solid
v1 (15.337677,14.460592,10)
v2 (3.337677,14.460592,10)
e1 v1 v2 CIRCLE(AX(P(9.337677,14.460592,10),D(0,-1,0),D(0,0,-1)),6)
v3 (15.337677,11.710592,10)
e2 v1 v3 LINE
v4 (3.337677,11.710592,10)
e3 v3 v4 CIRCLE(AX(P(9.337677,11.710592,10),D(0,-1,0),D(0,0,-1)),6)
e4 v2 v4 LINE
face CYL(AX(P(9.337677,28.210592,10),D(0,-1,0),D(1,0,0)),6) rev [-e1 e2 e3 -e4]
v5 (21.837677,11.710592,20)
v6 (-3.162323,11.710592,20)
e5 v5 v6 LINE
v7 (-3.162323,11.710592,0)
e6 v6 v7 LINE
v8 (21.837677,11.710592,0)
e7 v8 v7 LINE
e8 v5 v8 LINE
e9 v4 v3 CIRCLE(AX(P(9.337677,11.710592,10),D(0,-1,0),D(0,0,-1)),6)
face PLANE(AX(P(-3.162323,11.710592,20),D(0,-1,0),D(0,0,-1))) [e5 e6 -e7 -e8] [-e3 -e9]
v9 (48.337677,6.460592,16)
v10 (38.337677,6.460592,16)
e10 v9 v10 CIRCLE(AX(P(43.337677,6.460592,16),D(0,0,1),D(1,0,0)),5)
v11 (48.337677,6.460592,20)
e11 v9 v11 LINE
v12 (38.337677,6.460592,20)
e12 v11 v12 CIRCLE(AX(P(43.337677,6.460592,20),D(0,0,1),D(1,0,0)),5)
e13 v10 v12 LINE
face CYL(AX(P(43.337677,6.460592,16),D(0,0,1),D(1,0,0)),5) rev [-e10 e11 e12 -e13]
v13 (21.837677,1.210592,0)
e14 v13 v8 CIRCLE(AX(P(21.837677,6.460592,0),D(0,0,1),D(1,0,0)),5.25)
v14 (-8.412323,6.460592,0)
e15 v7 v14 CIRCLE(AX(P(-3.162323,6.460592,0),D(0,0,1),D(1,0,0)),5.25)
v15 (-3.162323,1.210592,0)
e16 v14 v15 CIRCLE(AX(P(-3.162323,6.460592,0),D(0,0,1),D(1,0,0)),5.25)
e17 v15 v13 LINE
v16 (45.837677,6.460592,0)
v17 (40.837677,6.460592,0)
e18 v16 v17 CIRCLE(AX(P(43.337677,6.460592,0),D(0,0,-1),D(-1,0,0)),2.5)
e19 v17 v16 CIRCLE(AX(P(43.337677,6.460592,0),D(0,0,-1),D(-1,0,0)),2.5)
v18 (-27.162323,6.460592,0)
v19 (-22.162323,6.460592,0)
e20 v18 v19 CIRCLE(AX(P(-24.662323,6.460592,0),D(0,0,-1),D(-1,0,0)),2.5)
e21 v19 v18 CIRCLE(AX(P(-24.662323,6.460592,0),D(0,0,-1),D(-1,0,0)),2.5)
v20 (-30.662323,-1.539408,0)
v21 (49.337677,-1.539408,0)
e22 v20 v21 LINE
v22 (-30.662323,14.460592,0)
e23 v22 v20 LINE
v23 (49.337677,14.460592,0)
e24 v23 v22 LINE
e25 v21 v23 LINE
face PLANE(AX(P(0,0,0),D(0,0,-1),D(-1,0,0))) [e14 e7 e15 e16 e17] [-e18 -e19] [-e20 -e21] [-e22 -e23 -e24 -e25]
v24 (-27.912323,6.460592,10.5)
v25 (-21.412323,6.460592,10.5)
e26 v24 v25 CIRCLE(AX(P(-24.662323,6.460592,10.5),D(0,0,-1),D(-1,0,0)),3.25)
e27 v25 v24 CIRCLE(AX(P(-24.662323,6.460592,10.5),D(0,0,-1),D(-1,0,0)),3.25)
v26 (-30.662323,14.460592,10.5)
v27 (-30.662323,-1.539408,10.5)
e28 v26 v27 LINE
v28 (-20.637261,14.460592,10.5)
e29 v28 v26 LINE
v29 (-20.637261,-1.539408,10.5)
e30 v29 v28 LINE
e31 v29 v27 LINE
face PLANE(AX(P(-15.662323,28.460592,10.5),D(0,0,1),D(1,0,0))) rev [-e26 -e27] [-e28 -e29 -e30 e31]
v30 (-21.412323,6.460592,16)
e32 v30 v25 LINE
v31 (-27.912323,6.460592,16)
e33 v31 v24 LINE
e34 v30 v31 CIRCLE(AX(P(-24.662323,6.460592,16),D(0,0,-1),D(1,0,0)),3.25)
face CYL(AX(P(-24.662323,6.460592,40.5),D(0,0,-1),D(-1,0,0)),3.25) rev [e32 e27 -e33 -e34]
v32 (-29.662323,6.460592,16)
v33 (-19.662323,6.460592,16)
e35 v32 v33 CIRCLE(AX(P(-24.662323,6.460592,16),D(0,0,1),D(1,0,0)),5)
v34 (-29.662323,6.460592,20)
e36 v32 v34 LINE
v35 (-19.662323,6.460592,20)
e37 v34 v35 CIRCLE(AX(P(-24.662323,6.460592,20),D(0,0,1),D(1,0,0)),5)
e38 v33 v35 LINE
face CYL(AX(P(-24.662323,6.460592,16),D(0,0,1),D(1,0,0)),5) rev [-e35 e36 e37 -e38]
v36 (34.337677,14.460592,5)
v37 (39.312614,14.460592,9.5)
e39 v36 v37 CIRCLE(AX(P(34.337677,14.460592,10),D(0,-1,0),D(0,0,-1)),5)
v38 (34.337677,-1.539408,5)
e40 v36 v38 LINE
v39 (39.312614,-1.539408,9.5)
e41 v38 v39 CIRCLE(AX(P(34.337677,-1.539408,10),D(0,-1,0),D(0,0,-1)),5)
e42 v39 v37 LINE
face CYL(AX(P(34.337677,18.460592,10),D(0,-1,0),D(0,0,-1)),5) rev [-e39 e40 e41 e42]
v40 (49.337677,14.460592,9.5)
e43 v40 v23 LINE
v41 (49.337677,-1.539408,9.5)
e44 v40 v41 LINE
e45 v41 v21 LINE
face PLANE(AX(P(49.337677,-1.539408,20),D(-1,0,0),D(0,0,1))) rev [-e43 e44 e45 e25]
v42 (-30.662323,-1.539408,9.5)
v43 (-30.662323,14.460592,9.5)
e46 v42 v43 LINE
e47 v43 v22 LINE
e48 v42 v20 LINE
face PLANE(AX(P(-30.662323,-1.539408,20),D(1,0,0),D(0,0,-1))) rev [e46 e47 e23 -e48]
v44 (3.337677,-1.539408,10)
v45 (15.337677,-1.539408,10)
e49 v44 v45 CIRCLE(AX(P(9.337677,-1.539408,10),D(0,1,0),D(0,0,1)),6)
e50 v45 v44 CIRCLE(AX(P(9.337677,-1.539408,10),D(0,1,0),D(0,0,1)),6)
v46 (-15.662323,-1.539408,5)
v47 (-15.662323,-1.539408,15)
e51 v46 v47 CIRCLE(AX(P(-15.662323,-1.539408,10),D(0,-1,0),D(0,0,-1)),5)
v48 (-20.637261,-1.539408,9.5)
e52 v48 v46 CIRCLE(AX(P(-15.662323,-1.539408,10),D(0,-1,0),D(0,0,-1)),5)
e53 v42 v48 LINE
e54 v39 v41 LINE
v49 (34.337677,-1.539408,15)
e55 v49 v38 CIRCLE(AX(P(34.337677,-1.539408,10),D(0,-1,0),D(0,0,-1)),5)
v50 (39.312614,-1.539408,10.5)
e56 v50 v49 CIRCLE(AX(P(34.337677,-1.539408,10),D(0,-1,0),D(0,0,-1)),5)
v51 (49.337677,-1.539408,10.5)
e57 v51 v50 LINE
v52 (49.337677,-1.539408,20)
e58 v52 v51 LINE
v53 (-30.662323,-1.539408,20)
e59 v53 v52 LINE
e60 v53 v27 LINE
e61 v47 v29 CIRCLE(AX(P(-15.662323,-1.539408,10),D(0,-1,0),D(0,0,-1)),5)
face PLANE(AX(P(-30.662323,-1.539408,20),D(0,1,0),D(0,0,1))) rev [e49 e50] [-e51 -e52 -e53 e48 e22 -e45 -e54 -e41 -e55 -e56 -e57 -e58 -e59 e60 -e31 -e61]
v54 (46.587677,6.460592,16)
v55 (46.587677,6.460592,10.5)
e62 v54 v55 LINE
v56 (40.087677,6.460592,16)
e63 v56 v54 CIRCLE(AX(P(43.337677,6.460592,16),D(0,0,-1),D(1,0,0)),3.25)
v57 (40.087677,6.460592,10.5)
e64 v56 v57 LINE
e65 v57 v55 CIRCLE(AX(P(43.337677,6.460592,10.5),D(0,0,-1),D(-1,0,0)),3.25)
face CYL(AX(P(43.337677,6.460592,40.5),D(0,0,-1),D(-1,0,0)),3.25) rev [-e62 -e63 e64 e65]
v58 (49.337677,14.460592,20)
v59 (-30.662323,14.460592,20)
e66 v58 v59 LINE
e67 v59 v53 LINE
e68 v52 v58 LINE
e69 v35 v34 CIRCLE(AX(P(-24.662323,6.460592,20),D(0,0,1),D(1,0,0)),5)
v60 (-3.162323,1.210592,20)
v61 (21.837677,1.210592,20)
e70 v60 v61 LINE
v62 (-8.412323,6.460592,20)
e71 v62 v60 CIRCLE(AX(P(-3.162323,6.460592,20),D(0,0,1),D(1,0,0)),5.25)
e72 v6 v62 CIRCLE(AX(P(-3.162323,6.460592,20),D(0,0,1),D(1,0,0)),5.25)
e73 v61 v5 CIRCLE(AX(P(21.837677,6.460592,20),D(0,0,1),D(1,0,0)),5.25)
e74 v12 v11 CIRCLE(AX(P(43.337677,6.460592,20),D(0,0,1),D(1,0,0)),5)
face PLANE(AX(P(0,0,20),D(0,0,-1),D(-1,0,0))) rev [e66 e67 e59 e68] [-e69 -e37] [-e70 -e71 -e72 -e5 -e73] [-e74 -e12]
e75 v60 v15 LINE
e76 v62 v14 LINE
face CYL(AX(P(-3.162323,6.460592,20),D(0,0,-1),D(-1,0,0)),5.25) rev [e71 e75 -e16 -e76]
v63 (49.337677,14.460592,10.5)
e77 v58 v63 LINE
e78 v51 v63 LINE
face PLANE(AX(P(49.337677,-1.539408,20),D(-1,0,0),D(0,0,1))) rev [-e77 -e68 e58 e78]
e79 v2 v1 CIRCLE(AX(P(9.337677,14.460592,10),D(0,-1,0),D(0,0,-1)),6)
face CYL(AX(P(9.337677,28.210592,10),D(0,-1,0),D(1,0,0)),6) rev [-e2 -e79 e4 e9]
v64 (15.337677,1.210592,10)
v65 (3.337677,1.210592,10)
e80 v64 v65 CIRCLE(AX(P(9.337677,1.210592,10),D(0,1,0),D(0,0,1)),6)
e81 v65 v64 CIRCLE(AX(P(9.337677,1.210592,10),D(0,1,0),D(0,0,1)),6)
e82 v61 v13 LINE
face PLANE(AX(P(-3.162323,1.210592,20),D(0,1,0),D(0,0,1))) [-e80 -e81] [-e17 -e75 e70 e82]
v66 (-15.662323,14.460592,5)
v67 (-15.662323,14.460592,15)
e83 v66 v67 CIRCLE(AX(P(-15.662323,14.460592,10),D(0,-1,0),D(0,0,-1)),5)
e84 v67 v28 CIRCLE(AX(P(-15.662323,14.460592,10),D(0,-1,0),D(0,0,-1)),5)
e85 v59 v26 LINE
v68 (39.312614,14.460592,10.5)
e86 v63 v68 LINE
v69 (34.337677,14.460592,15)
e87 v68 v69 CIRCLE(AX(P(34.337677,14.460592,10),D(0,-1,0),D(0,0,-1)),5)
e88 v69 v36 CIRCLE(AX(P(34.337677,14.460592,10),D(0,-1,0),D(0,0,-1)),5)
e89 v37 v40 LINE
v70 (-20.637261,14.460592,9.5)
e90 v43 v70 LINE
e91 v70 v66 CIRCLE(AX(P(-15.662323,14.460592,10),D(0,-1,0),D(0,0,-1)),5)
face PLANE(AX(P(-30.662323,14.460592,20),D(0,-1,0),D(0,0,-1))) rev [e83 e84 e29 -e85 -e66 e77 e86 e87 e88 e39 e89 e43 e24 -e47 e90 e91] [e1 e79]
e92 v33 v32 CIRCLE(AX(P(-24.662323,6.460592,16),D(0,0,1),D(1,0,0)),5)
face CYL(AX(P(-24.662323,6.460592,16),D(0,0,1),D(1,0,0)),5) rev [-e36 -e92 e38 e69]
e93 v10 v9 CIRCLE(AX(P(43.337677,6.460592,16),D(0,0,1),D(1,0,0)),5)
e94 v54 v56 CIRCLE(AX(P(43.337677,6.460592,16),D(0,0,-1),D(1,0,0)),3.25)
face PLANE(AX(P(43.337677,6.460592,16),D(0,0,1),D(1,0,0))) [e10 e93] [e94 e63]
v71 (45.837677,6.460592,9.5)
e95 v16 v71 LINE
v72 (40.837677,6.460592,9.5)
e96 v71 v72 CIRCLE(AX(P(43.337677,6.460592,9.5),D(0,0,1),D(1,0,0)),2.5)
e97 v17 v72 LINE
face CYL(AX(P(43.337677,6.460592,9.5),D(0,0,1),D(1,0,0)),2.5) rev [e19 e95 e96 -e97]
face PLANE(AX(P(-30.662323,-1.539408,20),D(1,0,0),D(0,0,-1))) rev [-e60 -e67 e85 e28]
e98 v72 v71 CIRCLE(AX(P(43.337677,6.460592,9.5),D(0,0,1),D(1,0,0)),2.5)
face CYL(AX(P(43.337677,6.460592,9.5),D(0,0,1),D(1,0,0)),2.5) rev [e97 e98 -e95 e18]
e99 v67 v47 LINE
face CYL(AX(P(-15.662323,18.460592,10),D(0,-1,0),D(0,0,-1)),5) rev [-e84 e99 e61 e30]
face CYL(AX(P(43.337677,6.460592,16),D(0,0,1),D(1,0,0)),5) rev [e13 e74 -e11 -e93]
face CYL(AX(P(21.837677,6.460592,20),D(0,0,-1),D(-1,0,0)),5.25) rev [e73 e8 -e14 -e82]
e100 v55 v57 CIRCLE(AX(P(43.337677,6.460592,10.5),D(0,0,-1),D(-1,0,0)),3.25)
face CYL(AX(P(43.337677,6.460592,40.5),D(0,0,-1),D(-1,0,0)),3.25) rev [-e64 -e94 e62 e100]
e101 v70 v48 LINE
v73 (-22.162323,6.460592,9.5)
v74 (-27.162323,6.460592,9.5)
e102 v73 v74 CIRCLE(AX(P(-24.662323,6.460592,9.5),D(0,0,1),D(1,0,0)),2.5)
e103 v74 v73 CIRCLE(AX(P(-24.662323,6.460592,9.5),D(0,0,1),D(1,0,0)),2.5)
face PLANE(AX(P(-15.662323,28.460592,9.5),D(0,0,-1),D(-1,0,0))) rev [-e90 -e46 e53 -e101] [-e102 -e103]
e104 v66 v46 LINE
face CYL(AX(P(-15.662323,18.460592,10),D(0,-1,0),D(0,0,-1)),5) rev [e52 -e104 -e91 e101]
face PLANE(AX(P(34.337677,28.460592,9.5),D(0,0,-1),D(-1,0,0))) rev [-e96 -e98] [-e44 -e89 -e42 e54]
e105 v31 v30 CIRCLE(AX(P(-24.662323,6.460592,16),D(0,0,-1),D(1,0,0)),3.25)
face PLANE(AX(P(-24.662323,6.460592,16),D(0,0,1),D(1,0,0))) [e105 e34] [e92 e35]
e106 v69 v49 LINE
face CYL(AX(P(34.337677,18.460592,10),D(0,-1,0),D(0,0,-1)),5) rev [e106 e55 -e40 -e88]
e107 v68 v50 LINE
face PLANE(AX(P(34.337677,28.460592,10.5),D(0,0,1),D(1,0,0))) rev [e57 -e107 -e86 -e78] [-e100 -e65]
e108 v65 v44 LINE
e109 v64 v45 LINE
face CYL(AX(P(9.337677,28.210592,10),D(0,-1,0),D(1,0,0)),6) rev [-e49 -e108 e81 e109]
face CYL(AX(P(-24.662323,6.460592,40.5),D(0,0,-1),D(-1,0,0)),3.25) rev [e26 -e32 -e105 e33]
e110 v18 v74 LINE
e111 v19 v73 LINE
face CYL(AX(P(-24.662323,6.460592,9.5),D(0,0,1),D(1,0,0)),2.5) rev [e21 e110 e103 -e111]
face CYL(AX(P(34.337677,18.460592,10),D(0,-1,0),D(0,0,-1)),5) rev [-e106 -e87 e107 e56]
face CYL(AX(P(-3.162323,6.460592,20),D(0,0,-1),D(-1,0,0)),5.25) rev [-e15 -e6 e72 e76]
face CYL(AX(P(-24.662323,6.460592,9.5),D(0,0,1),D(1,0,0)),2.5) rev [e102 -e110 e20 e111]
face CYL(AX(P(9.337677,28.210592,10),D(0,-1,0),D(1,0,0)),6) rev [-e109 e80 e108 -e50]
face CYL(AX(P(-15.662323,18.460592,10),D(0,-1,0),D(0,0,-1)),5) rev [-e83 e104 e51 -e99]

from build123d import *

# Parameters (mm, degrees)
SKETCH1_W                  = 80
SKETCH1_H                  = 16
BOSS_EXTRUDE1_DEPTH        = 20
SKETCH2_R                  = 5
CUT_EXTRUDE1_DEPTH         = 20
SKETCH4_R                  = 6
CUT_EXTRUDE2_DEPTH         = 16.5
SKETCH5_W                  = 29.106163607
SKETCH5_H                  = 1
SKETCH5_W_2                = 37.036491662
CUT_EXTRUDE3_DEPTH         = 30
M6_TAPPED_HOLE1_AT_2_COUNT = 2
M6_TAPPED_HOLE1_AT_2_PITCH = 68
SKETCH8_R                  = 3.25
CUT_EXTRUDE4_DEPTH         = 30
SKETCH9_R                  = 5
CUT_EXTRUDE5_DEPTH         = 4


with BuildPart() as part:
    # Sketch1 → Boss-Extrude1 (new body)
    with BuildSketch(Plane.XY):
        with Locations((9.337676654, 6.4605919)):
            Rectangle(SKETCH1_W, SKETCH1_H)
        with BuildLine():
            Line((-3.162323346, 11.7105919), (21.837676654, 11.7105919))
            ThreePointArc((21.837676654, 11.7105919), (27.087676654, 6.4605919), (21.837676654, 1.2105919))
            Line((21.837676654, 1.2105919), (-3.162323346, 1.2105919))
            ThreePointArc((-3.162323346, 1.2105919), (-8.412323346, 6.4605919), (-3.162323346, 11.7105919))
        make_face(mode=Mode.SUBTRACT)
    extrude(amount=BOSS_EXTRUDE1_DEPTH)

    # Sketch2 → Cut-Extrude1 (cut)
    with BuildSketch(Plane.XZ.offset(1.5394081)):
        with Locations(Location((34.337676654, 10, 0), (0, 0, 270))):
            Circle(SKETCH2_R)
        with Locations(Location((-15.662323346, 10, 0), (0, 0, 270))):
            Circle(SKETCH2_R)
    extrude(amount=-CUT_EXTRUDE1_DEPTH, mode=Mode.SUBTRACT)

    # Sketch4 → Cut-Extrude2 (cut, symmetric)
    with BuildSketch(Plane.XZ.offset(-11.7105919)):
        with Locations(Location((9.337676654, 10, 0), (0, 0, 270))):
            Circle(SKETCH4_R)
    extrude(amount=CUT_EXTRUDE2_DEPTH, both=True, mode=Mode.SUBTRACT)

    # Sketch5 → Cut-Extrude3 (cut)
    with BuildSketch(Plane.XZ.offset(1.5394081)):
        with Locations((48.890758457, 10)):
            Rectangle(SKETCH5_W, SKETCH5_H)
        with Locations((-34.180569177, 10)):
            Rectangle(SKETCH5_W_2, SKETCH5_H)
    extrude(amount=-CUT_EXTRUDE3_DEPTH, mode=Mode.SUBTRACT)

    # Sketch6 → M6 Tapped Hole1 (revolve, cut)
    with BuildSketch(Plane(origin=(43.337676654, 6.4605919, 9.5), x_dir=(0, -1, 0), z_dir=(1, 0, 0))):
        Polygon((0, 0), (0, 18.502151548), (2.5, 17), (2.5, 0), align=None)
    m6_tapped_hole1 = revolve(axis=Axis((43.337676654, 6.4605919, 15.85), (0, 0, -1)), mode=Mode.SUBTRACT)

    # M6 Tapped Hole1 at 2: M6 Tapped Hole1 ×2
    with Locations(*[(-i * M6_TAPPED_HOLE1_AT_2_PITCH, 0, 0) for i in range(1, M6_TAPPED_HOLE1_AT_2_COUNT)]):
        add(m6_tapped_hole1, mode=Mode.SUBTRACT)

    # Sketch8 → Cut-Extrude4 (cut)
    with BuildSketch(Plane(origin=(0, 0, 10.5), x_dir=(-1, 0, 0), z_dir=(0, 0, -1))):
        with Locations((24.662323346, 6.4605919)):
            Circle(SKETCH8_R)
        with Locations((-43.337676654, 6.4605919)):
            Circle(SKETCH8_R)
    extrude(amount=-CUT_EXTRUDE4_DEPTH, mode=Mode.SUBTRACT)

    # Sketch9 → Cut-Extrude5 (cut)
    with BuildSketch(Plane.XY.offset(20)):
        with Locations((43.337676654, 6.4605919)):
            Circle(SKETCH9_R)
        with Locations((-24.662323346, 6.4605919)):
            Circle(SKETCH9_R)
    extrude(amount=-CUT_EXTRUDE5_DEPTH, mode=Mode.SUBTRACT)


solid = part.part
